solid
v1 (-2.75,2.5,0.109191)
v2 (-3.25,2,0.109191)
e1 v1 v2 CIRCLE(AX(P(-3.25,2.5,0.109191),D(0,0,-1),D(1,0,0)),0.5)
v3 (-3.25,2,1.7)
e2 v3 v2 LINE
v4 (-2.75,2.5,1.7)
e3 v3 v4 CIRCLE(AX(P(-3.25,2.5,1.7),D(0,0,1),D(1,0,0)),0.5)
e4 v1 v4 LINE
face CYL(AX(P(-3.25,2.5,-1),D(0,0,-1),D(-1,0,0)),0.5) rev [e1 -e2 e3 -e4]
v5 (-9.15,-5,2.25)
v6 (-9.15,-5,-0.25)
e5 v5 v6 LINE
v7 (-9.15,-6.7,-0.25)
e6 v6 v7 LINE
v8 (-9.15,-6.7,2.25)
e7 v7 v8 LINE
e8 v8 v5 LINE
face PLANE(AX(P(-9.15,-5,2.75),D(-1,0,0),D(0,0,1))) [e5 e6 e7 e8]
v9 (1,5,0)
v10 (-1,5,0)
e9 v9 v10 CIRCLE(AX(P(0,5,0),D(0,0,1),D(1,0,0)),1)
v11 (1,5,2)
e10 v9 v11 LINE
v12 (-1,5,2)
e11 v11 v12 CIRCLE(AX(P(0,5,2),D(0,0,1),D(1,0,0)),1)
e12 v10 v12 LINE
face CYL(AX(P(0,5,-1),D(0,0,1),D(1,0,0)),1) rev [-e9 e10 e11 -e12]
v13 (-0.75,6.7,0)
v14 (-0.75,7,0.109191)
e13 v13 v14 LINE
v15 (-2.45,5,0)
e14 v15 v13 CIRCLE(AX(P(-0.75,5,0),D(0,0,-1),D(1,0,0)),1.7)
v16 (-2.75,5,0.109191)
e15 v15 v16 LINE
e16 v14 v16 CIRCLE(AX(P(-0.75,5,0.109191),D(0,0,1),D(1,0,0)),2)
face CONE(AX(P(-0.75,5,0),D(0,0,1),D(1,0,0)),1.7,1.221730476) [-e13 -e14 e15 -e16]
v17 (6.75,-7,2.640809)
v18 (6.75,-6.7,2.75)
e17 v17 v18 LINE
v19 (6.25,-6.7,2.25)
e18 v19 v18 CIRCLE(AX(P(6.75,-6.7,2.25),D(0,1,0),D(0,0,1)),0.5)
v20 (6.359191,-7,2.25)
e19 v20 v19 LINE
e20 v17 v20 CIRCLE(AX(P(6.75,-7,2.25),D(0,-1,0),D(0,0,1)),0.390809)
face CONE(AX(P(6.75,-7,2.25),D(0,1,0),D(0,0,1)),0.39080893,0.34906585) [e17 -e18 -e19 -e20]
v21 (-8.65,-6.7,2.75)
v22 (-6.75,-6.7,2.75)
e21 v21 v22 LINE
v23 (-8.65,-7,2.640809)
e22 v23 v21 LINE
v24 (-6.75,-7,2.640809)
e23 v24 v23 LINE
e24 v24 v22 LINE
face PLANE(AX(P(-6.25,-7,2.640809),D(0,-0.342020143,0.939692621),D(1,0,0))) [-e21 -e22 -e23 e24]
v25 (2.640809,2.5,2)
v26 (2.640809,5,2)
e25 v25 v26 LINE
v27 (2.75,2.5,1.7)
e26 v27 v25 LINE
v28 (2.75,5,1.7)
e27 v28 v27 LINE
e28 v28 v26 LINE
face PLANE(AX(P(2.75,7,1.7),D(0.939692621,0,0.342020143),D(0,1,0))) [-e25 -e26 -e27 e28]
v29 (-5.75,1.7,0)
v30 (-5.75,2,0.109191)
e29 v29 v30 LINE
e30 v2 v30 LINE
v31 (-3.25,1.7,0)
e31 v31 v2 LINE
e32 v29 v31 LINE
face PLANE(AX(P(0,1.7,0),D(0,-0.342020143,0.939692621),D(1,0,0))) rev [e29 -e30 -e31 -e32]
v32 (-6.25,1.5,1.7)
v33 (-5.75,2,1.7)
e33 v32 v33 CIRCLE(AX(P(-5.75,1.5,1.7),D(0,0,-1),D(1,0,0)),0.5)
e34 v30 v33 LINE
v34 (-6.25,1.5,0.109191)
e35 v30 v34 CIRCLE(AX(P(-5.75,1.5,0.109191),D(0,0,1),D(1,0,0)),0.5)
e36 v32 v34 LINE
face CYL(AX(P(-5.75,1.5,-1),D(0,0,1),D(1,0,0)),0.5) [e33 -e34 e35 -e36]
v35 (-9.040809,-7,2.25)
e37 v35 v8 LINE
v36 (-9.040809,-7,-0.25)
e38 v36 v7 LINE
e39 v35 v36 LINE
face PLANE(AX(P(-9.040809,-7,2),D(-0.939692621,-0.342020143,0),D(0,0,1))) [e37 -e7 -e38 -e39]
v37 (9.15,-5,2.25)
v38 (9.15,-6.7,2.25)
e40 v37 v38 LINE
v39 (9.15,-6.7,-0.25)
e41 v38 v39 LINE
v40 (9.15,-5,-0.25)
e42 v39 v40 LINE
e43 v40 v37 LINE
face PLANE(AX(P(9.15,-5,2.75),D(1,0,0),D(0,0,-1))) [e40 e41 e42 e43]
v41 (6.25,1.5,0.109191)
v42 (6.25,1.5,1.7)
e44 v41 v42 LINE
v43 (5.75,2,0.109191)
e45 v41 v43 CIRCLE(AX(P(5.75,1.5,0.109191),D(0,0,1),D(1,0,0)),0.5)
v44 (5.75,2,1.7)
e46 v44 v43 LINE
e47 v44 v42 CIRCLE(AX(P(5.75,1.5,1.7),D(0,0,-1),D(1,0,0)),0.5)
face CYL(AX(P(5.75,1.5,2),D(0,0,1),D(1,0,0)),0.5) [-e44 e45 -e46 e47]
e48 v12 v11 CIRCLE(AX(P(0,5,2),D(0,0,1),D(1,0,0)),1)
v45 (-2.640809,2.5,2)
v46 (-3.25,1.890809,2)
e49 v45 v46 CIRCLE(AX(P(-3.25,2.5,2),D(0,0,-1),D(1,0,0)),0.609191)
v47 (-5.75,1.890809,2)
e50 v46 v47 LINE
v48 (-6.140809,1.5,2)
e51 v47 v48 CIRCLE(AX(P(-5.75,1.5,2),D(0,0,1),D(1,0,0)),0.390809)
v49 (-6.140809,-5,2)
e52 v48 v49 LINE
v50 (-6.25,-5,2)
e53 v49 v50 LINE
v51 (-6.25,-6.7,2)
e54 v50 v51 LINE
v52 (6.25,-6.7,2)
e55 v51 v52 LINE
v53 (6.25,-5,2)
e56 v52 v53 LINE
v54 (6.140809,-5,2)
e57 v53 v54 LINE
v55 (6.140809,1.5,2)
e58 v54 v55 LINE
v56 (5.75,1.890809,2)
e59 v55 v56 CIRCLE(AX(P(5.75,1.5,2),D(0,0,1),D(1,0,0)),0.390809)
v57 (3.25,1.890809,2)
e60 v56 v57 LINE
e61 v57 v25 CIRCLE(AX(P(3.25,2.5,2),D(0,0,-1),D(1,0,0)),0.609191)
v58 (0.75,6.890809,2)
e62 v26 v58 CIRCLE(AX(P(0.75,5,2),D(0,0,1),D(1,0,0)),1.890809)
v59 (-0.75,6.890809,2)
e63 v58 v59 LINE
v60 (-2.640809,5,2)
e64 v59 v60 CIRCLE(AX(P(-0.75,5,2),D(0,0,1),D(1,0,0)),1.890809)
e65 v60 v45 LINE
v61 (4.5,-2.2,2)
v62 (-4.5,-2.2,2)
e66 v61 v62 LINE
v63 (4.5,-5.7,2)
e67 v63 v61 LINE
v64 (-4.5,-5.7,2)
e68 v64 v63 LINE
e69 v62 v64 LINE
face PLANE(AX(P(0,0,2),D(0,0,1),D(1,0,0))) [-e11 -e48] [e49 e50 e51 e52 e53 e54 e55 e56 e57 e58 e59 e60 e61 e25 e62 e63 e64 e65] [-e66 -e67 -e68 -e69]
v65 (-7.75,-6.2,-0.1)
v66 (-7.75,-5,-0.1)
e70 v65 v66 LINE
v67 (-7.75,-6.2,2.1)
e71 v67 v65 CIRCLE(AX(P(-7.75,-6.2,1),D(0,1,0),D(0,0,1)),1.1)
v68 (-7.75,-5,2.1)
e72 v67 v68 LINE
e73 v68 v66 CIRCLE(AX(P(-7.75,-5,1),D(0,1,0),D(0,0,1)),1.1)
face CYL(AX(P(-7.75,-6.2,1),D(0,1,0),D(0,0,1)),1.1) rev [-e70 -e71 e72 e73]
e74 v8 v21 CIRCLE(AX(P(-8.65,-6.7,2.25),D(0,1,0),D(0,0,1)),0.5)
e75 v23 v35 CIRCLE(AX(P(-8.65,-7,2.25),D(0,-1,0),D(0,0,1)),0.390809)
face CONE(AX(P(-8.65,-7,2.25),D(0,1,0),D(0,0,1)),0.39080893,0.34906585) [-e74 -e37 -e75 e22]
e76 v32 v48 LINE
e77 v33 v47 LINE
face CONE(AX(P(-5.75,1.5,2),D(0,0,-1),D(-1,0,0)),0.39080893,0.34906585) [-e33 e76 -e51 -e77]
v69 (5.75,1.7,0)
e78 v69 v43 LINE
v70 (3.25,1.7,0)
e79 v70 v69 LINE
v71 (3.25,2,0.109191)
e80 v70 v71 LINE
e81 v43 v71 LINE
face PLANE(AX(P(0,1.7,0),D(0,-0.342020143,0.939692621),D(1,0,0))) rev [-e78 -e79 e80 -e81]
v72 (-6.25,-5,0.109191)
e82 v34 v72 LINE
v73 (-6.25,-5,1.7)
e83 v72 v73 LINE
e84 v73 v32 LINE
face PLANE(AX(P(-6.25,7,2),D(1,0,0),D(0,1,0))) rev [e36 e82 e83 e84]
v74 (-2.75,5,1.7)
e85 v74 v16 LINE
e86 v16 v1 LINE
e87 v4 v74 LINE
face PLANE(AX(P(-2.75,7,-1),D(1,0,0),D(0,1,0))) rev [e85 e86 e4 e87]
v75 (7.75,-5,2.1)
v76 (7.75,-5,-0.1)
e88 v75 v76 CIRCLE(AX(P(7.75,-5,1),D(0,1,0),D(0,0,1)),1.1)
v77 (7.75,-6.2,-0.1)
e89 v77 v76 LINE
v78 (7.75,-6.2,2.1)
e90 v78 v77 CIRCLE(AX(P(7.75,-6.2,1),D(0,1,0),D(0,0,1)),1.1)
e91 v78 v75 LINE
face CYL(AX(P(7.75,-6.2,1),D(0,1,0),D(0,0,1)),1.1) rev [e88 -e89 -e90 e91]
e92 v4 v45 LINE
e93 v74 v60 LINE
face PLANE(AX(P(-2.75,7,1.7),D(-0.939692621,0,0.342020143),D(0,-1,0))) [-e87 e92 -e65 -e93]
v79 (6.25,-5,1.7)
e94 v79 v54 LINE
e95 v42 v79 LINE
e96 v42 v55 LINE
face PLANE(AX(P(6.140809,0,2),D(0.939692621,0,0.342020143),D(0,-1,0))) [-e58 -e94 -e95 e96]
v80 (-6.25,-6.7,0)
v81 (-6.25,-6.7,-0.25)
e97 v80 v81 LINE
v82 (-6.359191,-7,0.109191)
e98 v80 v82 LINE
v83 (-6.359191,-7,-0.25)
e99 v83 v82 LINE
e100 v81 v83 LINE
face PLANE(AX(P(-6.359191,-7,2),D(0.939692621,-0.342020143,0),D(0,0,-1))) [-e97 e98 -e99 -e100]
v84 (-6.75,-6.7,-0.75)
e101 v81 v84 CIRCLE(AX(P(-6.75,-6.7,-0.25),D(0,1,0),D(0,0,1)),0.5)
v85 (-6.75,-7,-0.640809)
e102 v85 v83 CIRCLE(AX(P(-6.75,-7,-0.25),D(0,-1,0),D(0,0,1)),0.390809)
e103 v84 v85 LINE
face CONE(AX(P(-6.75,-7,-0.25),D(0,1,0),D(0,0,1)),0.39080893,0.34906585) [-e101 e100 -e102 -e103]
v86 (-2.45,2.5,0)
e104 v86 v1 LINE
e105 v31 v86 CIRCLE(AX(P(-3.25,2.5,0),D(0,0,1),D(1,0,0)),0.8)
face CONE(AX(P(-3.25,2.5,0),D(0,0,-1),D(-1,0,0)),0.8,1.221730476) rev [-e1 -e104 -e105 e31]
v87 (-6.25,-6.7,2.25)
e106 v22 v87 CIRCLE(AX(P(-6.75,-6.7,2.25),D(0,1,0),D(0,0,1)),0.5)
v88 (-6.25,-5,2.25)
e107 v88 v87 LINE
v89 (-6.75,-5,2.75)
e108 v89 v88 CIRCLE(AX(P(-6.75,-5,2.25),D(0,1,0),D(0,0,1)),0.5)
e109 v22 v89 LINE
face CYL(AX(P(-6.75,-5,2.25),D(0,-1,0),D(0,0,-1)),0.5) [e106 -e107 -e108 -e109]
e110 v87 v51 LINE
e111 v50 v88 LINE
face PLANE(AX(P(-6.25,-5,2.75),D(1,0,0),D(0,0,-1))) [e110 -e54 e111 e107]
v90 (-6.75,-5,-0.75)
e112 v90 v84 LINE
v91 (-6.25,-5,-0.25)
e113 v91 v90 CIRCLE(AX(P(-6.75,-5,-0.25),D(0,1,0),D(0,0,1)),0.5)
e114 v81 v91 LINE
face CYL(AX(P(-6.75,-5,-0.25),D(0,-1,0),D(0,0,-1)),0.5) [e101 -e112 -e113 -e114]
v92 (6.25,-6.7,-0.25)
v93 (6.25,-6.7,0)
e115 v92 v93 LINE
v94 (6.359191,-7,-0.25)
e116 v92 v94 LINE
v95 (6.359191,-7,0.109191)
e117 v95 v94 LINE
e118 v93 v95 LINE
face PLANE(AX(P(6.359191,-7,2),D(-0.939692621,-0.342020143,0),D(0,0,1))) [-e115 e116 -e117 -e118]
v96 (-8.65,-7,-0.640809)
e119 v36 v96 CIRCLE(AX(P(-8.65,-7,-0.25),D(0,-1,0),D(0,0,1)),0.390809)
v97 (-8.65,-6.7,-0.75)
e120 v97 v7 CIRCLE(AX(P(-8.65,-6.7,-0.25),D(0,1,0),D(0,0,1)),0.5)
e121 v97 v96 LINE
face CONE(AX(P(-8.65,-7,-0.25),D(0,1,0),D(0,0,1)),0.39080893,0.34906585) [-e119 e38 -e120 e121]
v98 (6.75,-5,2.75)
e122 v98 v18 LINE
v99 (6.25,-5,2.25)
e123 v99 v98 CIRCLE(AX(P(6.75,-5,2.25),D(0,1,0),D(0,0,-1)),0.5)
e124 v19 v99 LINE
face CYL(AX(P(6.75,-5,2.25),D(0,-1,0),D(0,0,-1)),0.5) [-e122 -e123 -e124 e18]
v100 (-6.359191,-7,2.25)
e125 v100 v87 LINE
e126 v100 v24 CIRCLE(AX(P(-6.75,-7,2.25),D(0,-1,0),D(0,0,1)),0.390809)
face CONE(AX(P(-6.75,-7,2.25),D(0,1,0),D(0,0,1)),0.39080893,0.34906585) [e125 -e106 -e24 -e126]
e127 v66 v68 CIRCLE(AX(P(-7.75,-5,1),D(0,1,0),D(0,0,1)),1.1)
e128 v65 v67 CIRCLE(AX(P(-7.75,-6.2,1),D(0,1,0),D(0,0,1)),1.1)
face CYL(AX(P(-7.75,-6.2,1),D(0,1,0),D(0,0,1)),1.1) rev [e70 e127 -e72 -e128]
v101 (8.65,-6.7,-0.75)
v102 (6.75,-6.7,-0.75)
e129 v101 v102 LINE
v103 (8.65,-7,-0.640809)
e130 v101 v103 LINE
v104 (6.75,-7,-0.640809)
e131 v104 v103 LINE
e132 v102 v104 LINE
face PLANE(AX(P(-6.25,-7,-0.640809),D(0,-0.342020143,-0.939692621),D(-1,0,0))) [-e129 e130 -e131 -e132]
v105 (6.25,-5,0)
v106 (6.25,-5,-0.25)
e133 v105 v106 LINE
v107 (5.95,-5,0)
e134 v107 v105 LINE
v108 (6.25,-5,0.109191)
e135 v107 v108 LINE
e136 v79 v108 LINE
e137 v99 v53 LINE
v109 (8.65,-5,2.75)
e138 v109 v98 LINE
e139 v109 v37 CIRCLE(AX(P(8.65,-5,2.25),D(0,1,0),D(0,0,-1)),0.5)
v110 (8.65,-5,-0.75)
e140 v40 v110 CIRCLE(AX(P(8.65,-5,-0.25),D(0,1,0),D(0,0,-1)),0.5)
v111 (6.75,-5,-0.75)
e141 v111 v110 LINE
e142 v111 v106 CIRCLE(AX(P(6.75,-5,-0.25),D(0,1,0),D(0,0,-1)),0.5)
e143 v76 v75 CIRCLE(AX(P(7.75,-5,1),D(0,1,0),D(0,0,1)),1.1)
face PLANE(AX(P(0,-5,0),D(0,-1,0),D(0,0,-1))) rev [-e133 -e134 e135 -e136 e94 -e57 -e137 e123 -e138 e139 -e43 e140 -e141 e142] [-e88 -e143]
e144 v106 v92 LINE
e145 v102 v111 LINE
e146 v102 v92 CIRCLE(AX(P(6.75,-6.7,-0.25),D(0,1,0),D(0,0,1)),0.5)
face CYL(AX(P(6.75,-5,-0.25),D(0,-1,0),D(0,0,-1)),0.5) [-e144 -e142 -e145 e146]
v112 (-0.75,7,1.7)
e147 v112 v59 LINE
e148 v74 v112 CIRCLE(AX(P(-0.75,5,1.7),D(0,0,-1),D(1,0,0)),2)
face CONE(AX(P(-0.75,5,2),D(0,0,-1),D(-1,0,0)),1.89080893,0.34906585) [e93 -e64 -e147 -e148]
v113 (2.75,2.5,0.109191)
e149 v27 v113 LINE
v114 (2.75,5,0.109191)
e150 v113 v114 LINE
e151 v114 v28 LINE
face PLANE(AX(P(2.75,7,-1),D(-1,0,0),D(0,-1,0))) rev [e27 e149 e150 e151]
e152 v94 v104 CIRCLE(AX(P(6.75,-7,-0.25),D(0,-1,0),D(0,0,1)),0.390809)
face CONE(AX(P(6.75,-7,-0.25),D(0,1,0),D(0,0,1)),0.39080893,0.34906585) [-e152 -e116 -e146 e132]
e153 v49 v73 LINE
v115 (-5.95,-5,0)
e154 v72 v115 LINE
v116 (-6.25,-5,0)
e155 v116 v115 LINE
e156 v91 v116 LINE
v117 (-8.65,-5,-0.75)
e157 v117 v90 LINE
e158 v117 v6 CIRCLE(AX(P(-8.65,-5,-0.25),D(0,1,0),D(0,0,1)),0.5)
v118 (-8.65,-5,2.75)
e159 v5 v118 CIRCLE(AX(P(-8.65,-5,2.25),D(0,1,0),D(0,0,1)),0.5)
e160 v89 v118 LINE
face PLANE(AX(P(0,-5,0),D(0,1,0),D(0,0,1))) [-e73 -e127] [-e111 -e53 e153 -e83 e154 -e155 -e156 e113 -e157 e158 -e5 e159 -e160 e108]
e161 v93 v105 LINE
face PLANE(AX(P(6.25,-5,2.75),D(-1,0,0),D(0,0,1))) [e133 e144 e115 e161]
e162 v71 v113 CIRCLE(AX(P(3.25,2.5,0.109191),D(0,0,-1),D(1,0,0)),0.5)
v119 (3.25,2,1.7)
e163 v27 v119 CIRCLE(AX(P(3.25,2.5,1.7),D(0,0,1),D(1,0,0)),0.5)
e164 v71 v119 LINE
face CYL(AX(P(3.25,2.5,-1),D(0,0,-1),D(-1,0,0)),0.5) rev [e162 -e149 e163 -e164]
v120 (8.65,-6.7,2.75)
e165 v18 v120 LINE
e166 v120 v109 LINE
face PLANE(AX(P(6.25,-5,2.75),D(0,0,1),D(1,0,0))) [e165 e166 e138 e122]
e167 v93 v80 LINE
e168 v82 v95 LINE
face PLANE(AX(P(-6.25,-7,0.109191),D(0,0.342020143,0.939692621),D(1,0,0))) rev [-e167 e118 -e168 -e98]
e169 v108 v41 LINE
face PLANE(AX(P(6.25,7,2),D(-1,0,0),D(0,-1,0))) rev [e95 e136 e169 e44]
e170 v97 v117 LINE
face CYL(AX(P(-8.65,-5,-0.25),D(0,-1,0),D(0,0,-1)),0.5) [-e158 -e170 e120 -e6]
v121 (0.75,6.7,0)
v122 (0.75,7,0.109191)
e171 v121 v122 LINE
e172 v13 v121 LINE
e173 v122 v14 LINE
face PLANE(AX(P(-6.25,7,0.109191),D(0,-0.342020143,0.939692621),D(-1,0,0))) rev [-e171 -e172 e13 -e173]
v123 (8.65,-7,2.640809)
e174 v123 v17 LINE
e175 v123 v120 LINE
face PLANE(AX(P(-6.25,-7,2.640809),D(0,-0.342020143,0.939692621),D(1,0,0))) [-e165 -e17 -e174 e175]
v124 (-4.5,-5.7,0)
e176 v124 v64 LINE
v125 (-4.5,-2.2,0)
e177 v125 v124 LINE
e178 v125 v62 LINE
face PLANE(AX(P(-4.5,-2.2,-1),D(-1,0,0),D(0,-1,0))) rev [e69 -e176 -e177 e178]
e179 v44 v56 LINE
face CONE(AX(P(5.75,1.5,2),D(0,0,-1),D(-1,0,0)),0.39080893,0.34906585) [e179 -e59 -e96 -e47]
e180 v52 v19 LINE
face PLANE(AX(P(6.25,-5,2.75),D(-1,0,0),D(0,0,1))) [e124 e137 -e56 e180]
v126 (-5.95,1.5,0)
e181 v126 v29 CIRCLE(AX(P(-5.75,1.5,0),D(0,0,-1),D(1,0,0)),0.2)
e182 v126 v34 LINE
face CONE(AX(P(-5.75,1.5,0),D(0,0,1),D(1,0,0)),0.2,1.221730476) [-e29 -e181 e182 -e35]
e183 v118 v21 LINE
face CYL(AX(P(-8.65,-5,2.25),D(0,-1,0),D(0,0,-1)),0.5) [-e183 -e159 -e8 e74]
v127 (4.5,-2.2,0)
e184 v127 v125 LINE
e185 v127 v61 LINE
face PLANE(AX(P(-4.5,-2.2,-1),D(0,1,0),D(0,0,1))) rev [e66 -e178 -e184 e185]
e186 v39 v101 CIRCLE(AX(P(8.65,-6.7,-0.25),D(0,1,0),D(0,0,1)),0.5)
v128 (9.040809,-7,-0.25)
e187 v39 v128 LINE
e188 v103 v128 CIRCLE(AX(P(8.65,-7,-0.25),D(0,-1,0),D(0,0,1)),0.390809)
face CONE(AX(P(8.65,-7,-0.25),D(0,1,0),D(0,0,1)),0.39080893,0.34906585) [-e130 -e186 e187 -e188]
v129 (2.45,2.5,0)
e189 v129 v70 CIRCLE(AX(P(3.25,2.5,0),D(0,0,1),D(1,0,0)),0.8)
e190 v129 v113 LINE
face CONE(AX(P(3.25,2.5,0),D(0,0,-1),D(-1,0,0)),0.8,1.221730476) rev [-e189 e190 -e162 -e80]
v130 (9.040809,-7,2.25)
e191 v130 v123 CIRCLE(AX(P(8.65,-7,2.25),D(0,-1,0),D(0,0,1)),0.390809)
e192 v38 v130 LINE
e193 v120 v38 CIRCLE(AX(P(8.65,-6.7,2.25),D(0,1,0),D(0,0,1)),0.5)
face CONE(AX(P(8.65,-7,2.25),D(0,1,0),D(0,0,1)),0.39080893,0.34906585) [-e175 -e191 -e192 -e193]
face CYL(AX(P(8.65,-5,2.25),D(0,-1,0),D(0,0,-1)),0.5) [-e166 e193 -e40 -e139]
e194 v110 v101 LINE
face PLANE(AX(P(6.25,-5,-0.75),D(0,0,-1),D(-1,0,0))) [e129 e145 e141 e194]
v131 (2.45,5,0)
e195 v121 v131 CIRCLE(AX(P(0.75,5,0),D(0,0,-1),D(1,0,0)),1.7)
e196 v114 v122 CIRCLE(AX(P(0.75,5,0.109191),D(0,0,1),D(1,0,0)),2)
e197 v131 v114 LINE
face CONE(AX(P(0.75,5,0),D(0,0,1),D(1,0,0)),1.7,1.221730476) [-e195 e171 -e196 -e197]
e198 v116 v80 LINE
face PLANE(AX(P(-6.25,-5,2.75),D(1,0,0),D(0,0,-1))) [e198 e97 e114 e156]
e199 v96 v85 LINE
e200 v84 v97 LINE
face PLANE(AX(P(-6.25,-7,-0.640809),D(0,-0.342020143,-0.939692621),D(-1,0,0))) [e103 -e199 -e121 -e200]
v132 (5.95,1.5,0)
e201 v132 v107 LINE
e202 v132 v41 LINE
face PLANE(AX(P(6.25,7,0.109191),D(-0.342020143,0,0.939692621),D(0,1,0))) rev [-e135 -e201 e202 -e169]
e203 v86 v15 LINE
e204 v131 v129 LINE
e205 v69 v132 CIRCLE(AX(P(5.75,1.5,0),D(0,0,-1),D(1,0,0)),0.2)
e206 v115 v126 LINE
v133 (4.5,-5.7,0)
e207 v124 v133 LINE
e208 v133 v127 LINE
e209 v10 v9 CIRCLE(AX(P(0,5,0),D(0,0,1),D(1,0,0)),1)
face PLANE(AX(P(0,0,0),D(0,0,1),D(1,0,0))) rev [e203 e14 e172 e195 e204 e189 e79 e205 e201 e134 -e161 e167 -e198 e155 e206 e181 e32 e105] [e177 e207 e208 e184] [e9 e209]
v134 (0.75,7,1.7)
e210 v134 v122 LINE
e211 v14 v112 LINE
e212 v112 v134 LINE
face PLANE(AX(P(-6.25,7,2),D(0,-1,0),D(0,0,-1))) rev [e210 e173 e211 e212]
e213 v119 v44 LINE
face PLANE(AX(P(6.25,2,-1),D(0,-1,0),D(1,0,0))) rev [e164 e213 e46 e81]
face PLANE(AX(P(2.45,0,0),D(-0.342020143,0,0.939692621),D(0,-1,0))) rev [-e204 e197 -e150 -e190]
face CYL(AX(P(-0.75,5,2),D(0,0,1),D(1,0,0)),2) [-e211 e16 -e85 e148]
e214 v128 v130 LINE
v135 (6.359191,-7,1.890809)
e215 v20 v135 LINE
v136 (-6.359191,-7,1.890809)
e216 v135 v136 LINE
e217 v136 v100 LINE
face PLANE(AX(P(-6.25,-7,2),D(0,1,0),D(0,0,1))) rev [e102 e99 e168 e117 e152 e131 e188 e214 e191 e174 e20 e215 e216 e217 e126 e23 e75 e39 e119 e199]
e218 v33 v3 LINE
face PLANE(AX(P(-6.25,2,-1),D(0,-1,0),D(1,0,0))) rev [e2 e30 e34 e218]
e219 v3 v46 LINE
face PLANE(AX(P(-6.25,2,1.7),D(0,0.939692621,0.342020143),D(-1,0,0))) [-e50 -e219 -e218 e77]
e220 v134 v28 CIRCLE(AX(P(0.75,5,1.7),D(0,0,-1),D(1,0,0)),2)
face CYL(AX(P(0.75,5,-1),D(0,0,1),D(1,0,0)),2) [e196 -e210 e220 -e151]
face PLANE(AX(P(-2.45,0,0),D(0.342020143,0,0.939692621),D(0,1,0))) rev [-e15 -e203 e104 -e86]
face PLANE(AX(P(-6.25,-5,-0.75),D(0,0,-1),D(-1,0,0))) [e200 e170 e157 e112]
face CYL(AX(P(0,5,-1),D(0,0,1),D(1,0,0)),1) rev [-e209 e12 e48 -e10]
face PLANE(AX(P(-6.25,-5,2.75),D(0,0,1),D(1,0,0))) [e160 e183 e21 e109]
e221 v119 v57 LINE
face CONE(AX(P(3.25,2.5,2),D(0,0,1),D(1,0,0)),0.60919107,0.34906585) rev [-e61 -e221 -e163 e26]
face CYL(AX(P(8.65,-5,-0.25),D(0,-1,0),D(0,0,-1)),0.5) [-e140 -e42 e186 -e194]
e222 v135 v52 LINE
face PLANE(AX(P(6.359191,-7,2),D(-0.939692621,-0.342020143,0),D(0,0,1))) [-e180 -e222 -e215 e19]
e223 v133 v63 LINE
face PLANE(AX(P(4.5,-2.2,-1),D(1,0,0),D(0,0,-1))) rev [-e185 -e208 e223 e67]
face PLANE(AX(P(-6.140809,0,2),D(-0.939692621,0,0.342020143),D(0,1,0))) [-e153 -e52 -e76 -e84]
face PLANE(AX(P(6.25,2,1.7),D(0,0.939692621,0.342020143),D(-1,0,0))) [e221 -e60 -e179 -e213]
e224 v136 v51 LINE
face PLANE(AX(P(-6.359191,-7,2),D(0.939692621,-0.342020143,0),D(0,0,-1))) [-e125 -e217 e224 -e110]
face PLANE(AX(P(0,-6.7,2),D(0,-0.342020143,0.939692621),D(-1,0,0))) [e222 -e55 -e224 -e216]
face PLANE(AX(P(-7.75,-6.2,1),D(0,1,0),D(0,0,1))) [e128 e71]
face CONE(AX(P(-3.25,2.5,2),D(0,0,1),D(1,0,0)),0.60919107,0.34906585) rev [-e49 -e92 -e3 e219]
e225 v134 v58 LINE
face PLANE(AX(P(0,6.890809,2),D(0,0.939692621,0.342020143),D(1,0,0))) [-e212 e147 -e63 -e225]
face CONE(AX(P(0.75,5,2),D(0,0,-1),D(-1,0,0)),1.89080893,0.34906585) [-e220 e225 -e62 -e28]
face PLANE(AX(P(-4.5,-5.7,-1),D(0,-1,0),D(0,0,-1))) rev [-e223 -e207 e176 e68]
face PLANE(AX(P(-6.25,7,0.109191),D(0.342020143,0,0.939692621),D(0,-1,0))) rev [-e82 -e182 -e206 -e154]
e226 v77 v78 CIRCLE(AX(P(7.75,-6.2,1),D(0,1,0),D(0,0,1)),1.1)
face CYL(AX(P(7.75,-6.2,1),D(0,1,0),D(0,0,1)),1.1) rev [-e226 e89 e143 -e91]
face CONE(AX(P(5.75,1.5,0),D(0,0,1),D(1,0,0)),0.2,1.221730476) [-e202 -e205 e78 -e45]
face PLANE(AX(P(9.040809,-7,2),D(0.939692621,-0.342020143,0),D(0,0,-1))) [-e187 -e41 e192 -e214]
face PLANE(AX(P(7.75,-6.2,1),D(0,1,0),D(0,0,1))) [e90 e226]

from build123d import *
from OCP.BRepFilletAPI import BRepFilletAPI_MakeChamfer

# Parameters (mm, degrees)
SKETCH1_W           = 12.5
SKETCH1_H           = 14
BOSS_EXTRUDE1_DEPTH = 2
SKETCH2_R           = 1
SKETCH2_W           = 9
SKETCH2_H           = 3.5
SKETCH2_W_2         = 3.5
SKETCH2_H_2         = 5
CUT_EXTRUDE1_DEPTH  = 3
FILLET1_R           = 2
SKETCH4_W           = 2.9
SKETCH4_H           = 3.5
BOSS_EXTRUDE2_DEPTH = 2
SKETCH5_R           = 1.1
CUT_EXTRUDE3_DEPTH  = 1.2
FILLET2_R           = 0.5
FILLET3_R           = 0.5
CHAMFER1_SIZE       = 0.3
CHAMFER1_SIZE2      = 0.10919107


with BuildPart() as part:
    # Sketch1 → Boss-Extrude1 (new body)
    with BuildSketch(Plane.XY):
        Rectangle(SKETCH1_W, SKETCH1_H)
    extrude(amount=BOSS_EXTRUDE1_DEPTH)

    # Sketch2 → Cut-Extrude1 (cut)
    with BuildSketch(Plane.XY.offset(2)):
        with Locations((0, 5)):
            Circle(SKETCH2_R)
        with Locations((0, -3.95)):
            Rectangle(SKETCH2_W, SKETCH2_H)
        with Locations((-4.5, 4.5)):
            Rectangle(SKETCH2_W_2, SKETCH2_H_2)
        with Locations((4.5, 4.5)):
            Rectangle(SKETCH2_W_2, SKETCH2_H_2)
    extrude(amount=-CUT_EXTRUDE1_DEPTH, mode=Mode.SUBTRACT)

    # Fillet1
    fillet1_edges = [part.edges().sort_by_distance(p)[0] for p in [
        (-2.75, 7, 1),
        (2.75, 7, 1),
    ]]
    fillet(fillet1_edges, radius=FILLET1_R)

    # Sketch4 → Boss-Extrude2 (add)
    with BuildSketch(Plane.XZ.offset(7)):
        with Locations((-7.7, 1)):
            Rectangle(SKETCH4_W, SKETCH4_H)
        with Locations((7.7, 1)):
            Rectangle(SKETCH4_W, SKETCH4_H)
    extrude(amount=-BOSS_EXTRUDE2_DEPTH)

    # Sketch5 → Cut-Extrude3 (cut)
    with BuildSketch(Plane(origin=(0, -5, 0), x_dir=(1, 0, 0), z_dir=(0, 1, 0))):
        with Locations(Location((-7.75, -1, 0), (0, 0, 270))):
            Circle(SKETCH5_R)
        with Locations(Location((7.75, -1, 0), (0, 0, 270))):
            Circle(SKETCH5_R)
    extrude(amount=-CUT_EXTRUDE3_DEPTH, mode=Mode.SUBTRACT)

    # Fillet2
    fillet2_edges = [part.edges().sort_by_distance(p)[0] for p in [
        (6.25, -6, -0.75),
        (6.25, -6, 2.75),
        (9.15, -6, 2.75),
        (9.15, -6, -0.75),
        (-6.25, 2, 1),
        (6.25, 2, 1),
        (-6.25, -6, 2.75),
        (-6.25, -6, -0.75),
        (-9.15, -6, -0.75),
        (-9.15, -6, 2.75),
    ]]
    fillet(fillet2_edges, radius=FILLET2_R)

    # Fillet3
    fillet3_edges = [part.edges().sort_by_distance(p)[0] for p in [
        (-2.75, 2, 1),
        (2.75, 2, 1),
    ]]
    fillet(fillet3_edges, radius=FILLET3_R)

    # Chamfer1: one chamfer whose edges measure the first distance from different faces: ONE call of the kernel's chamfer builder (chamfer() names one face for all edges)
    chamfer1_edges_1 = [part.edges().sort_by_distance(p)[0] for p in [
        (-9.003553391, -7, -0.603553391),
    ]]
    chamfer1_side_1 = [part.faces().sort_by_distance(p)[0] for p in [
        (-9.003553391, -6, -0.603553391),
    ]]
    chamfer1_edges_2 = [part.edges().sort_by_distance(p)[0] for p in [
        (-9.15, -7, 1),
    ]]
    chamfer1_side_2 = [part.faces().sort_by_distance(p)[0] for p in [
        (-9.15, -6, 1),
    ]]
    chamfer1_edges_3 = [part.edges().sort_by_distance(p)[0] for p in [
        (-9.003553391, -7, 2.603553391),
    ]]
    chamfer1_side_3 = [part.faces().sort_by_distance(p)[0] for p in [
        (-9.003553391, -6, 2.603553391),
    ]]
    chamfer1_edges_4 = [part.edges().sort_by_distance(p)[0] for p in [
        (-7.7, -7, 2.75),
    ]]
    chamfer1_side_4 = [part.faces().sort_by_distance(p)[0] for p in [
        (-7.7, -6, 2.75),
    ]]
    chamfer1_edges_5 = [part.edges().sort_by_distance(p)[0] for p in [
        (-6.396446609, -7, 2.603553391),
    ]]
    chamfer1_side_5 = [part.faces().sort_by_distance(p)[0] for p in [
        (-6.396446609, -6, 2.603553391),
    ]]
    chamfer1_edges_6 = [part.edges().sort_by_distance(p)[0] for p in [
        (-6.25, -7, 2.125),
    ]]
    chamfer1_side_6 = [part.faces().sort_by_distance(p)[0] for p in [
        (-6.25, -6, 2.125),
    ]]
    chamfer1_edges_7 = [part.edges().sort_by_distance(p)[0] for p in [
        (0, -7, 2),
    ]]
    chamfer1_side_7 = [part.faces().sort_by_distance(p)[0] for p in [
        (0, -0.579012096, 2),
    ]]
    chamfer1_edges_8 = [part.edges().sort_by_distance(p)[0] for p in [
        (6.25, -7, 2.125),
    ]]
    chamfer1_side_8 = [part.faces().sort_by_distance(p)[0] for p in [
        (6.25, -6, 2.125),
    ]]
    chamfer1_edges_9 = [part.edges().sort_by_distance(p)[0] for p in [
        (6.396446609, -7, 2.603553391),
    ]]
    chamfer1_side_9 = [part.faces().sort_by_distance(p)[0] for p in [
        (6.396446609, -6, 2.603553391),
    ]]
    chamfer1_edges_10 = [part.edges().sort_by_distance(p)[0] for p in [
        (7.7, -7, 2.75),
    ]]
    chamfer1_side_10 = [part.faces().sort_by_distance(p)[0] for p in [
        (7.7, -6, 2.75),
    ]]
    chamfer1_edges_11 = [part.edges().sort_by_distance(p)[0] for p in [
        (9.003553391, -7, 2.603553391),
    ]]
    chamfer1_side_11 = [part.faces().sort_by_distance(p)[0] for p in [
        (9.003553391, -6, 2.603553391),
    ]]
    chamfer1_edges_12 = [part.edges().sort_by_distance(p)[0] for p in [
        (9.15, -7, 1),
    ]]
    chamfer1_side_12 = [part.faces().sort_by_distance(p)[0] for p in [
        (9.15, -6, 1),
    ]]
    chamfer1_edges_13 = [part.edges().sort_by_distance(p)[0] for p in [
        (9.003553391, -7, -0.603553391),
    ]]
    chamfer1_side_13 = [part.faces().sort_by_distance(p)[0] for p in [
        (9.003553391, -6, -0.603553391),
    ]]
    chamfer1_edges_14 = [part.edges().sort_by_distance(p)[0] for p in [
        (7.7, -7, -0.75),
    ]]
    chamfer1_side_14 = [part.faces().sort_by_distance(p)[0] for p in [
        (7.7, -6, -0.75),
    ]]
    chamfer1_edges_15 = [part.edges().sort_by_distance(p)[0] for p in [
        (6.396446609, -7, -0.603553391),
    ]]
    chamfer1_side_15 = [part.faces().sort_by_distance(p)[0] for p in [
        (6.396446609, -6, -0.603553391),
    ]]
    chamfer1_edges_16 = [part.edges().sort_by_distance(p)[0] for p in [
        (6.25, -7, -0.125),
    ]]
    chamfer1_side_16 = [part.faces().sort_by_distance(p)[0] for p in [
        (6.25, -6, -0.125),
    ]]
    chamfer1_edges_17 = [part.edges().sort_by_distance(p)[0] for p in [
        (0, -7, 0),
        (6.25, -1.75, 0),
        (6.103553391, 1.853553391, 0),
        (2.896446609, 2.146446609, 0),
        (2.75, 3.75, 0),
        (2.164213562, 6.414213562, 0),
        (0, 7, 0),
        (-2.164213562, 6.414213562, 0),
        (-2.75, 3.75, 0),
        (-2.896446609, 2.146446609, 0),
        (-6.103553391, 1.853553391, 0),
        (-6.25, -1.75, 0),
        (4.5, 2, 0),
        (-4.5, 2, 0),
    ]]
    chamfer1_side_17 = [part.faces().sort_by_distance(p)[0] for p in [
        (0, -0.579012096, 0),
    ]]
    chamfer1_edges_18 = [part.edges().sort_by_distance(p)[0] for p in [
        (-6.25, -7, -0.125),
    ]]
    chamfer1_side_18 = [part.faces().sort_by_distance(p)[0] for p in [
        (-6.25, -6, -0.125),
    ]]
    chamfer1_edges_19 = [part.edges().sort_by_distance(p)[0] for p in [
        (-6.396446609, -7, -0.603553391),
    ]]
    chamfer1_side_19 = [part.faces().sort_by_distance(p)[0] for p in [
        (-6.396446609, -6, -0.603553391),
    ]]
    chamfer1_edges_20 = [part.edges().sort_by_distance(p)[0] for p in [
        (-7.7, -7, -0.75),
    ]]
    chamfer1_side_20 = [part.faces().sort_by_distance(p)[0] for p in [
        (-7.7, -6, -0.75),
    ]]
    chamfer1_edges_21 = [part.edges().sort_by_distance(p)[0] for p in [
        (6.25, -1.75, 2),
    ]]
    chamfer1_side_21 = [part.faces().sort_by_distance(p)[0] for p in [
        (6.25, -1.75, 1),
    ]]
    chamfer1_edges_22 = [part.edges().sort_by_distance(p)[0] for p in [
        (6.103553391, 1.853553391, 2),
    ]]
    chamfer1_side_22 = [part.faces().sort_by_distance(p)[0] for p in [
        (6.103553391, 1.853553391, 1),
    ]]
    chamfer1_edges_23 = [part.edges().sort_by_distance(p)[0] for p in [
        (2.896446609, 2.146446609, 2),
    ]]
    chamfer1_side_23 = [part.faces().sort_by_distance(p)[0] for p in [
        (2.896446609, 2.146446609, 1),
    ]]
    chamfer1_edges_24 = [part.edges().sort_by_distance(p)[0] for p in [
        (2.75, 3.75, 2),
    ]]
    chamfer1_side_24 = [part.faces().sort_by_distance(p)[0] for p in [
        (2.75, 3.75, 1),
    ]]
    chamfer1_edges_25 = [part.edges().sort_by_distance(p)[0] for p in [
        (2.164213562, 6.414213562, 2),
    ]]
    chamfer1_side_25 = [part.faces().sort_by_distance(p)[0] for p in [
        (2.164213562, 6.414213562, 1),
    ]]
    chamfer1_edges_26 = [part.edges().sort_by_distance(p)[0] for p in [
        (0, 7, 2),
    ]]
    chamfer1_side_26 = [part.faces().sort_by_distance(p)[0] for p in [
        (0, 7, 1),
    ]]
    chamfer1_edges_27 = [part.edges().sort_by_distance(p)[0] for p in [
        (-2.164213562, 6.414213562, 2),
    ]]
    chamfer1_side_27 = [part.faces().sort_by_distance(p)[0] for p in [
        (-2.164213562, 6.414213562, 1),
    ]]
    chamfer1_edges_28 = [part.edges().sort_by_distance(p)[0] for p in [
        (-2.75, 3.75, 2),
    ]]
    chamfer1_side_28 = [part.faces().sort_by_distance(p)[0] for p in [
        (-2.75, 3.75, 1),
    ]]
    chamfer1_edges_29 = [part.edges().sort_by_distance(p)[0] for p in [
        (-2.896446609, 2.146446609, 2),
    ]]
    chamfer1_side_29 = [part.faces().sort_by_distance(p)[0] for p in [
        (-2.896446609, 2.146446609, 1),
    ]]
    chamfer1_edges_30 = [part.edges().sort_by_distance(p)[0] for p in [
        (-6.103553391, 1.853553391, 2),
    ]]
    chamfer1_side_30 = [part.faces().sort_by_distance(p)[0] for p in [
        (-6.103553391, 1.853553391, 1),
    ]]
    chamfer1_edges_31 = [part.edges().sort_by_distance(p)[0] for p in [
        (-6.25, -1.75, 2),
    ]]
    chamfer1_side_31 = [part.faces().sort_by_distance(p)[0] for p in [
        (-6.25, -1.75, 1),
    ]]
    chamfer1_edges_32 = [part.edges().sort_by_distance(p)[0] for p in [
        (4.5, 2, 2),
    ]]
    chamfer1_side_32 = [part.faces().sort_by_distance(p)[0] for p in [
        (4.5, 2, 1),
    ]]
    chamfer1_edges_33 = [part.edges().sort_by_distance(p)[0] for p in [
        (-4.5, 2, 2),
    ]]
    chamfer1_side_33 = [part.faces().sort_by_distance(p)[0] for p in [
        (-4.5, 2, 1),
    ]]
    chamfer1 = BRepFilletAPI_MakeChamfer(part.part.solid().wrapped)
    for e in chamfer1_edges_1:
        chamfer1.Add(CHAMFER1_SIZE, CHAMFER1_SIZE2, e.wrapped, chamfer1_side_1[0].wrapped)  # the first distance lies on this face
    for e in chamfer1_edges_2:
        chamfer1.Add(CHAMFER1_SIZE, CHAMFER1_SIZE2, e.wrapped, chamfer1_side_2[0].wrapped)  # the first distance lies on this face
    for e in chamfer1_edges_3:
        chamfer1.Add(CHAMFER1_SIZE, CHAMFER1_SIZE2, e.wrapped, chamfer1_side_3[0].wrapped)  # the first distance lies on this face
    for e in chamfer1_edges_4:
        chamfer1.Add(CHAMFER1_SIZE, CHAMFER1_SIZE2, e.wrapped, chamfer1_side_4[0].wrapped)  # the first distance lies on this face
    for e in chamfer1_edges_5:
        chamfer1.Add(CHAMFER1_SIZE, CHAMFER1_SIZE2, e.wrapped, chamfer1_side_5[0].wrapped)  # the first distance lies on this face
    for e in chamfer1_edges_6:
        chamfer1.Add(CHAMFER1_SIZE, CHAMFER1_SIZE2, e.wrapped, chamfer1_side_6[0].wrapped)  # the first distance lies on this face
    for e in chamfer1_edges_7:
        chamfer1.Add(CHAMFER1_SIZE, CHAMFER1_SIZE2, e.wrapped, chamfer1_side_7[0].wrapped)  # the first distance lies on this face
    for e in chamfer1_edges_8:
        chamfer1.Add(CHAMFER1_SIZE, CHAMFER1_SIZE2, e.wrapped, chamfer1_side_8[0].wrapped)  # the first distance lies on this face
    for e in chamfer1_edges_9:
        chamfer1.Add(CHAMFER1_SIZE, CHAMFER1_SIZE2, e.wrapped, chamfer1_side_9[0].wrapped)  # the first distance lies on this face
    for e in chamfer1_edges_10:
        chamfer1.Add(CHAMFER1_SIZE, CHAMFER1_SIZE2, e.wrapped, chamfer1_side_10[0].wrapped)  # the first distance lies on this face
    for e in chamfer1_edges_11:
        chamfer1.Add(CHAMFER1_SIZE, CHAMFER1_SIZE2, e.wrapped, chamfer1_side_11[0].wrapped)  # the first distance lies on this face
    for e in chamfer1_edges_12:
        chamfer1.Add(CHAMFER1_SIZE, CHAMFER1_SIZE2, e.wrapped, chamfer1_side_12[0].wrapped)  # the first distance lies on this face
    for e in chamfer1_edges_13:
        chamfer1.Add(CHAMFER1_SIZE, CHAMFER1_SIZE2, e.wrapped, chamfer1_side_13[0].wrapped)  # the first distance lies on this face
    for e in chamfer1_edges_14:
        chamfer1.Add(CHAMFER1_SIZE, CHAMFER1_SIZE2, e.wrapped, chamfer1_side_14[0].wrapped)  # the first distance lies on this face
    for e in chamfer1_edges_15:
        chamfer1.Add(CHAMFER1_SIZE, CHAMFER1_SIZE2, e.wrapped, chamfer1_side_15[0].wrapped)  # the first distance lies on this face
    for e in chamfer1_edges_16:
        chamfer1.Add(CHAMFER1_SIZE, CHAMFER1_SIZE2, e.wrapped, chamfer1_side_16[0].wrapped)  # the first distance lies on this face
    for e in chamfer1_edges_17:
        chamfer1.Add(CHAMFER1_SIZE, CHAMFER1_SIZE2, e.wrapped, chamfer1_side_17[0].wrapped)  # the first distance lies on this face
    for e in chamfer1_edges_18:
        chamfer1.Add(CHAMFER1_SIZE, CHAMFER1_SIZE2, e.wrapped, chamfer1_side_18[0].wrapped)  # the first distance lies on this face
    for e in chamfer1_edges_19:
        chamfer1.Add(CHAMFER1_SIZE, CHAMFER1_SIZE2, e.wrapped, chamfer1_side_19[0].wrapped)  # the first distance lies on this face
    for e in chamfer1_edges_20:
        chamfer1.Add(CHAMFER1_SIZE, CHAMFER1_SIZE2, e.wrapped, chamfer1_side_20[0].wrapped)  # the first distance lies on this face
    for e in chamfer1_edges_21:
        chamfer1.Add(CHAMFER1_SIZE, CHAMFER1_SIZE2, e.wrapped, chamfer1_side_21[0].wrapped)  # the first distance lies on this face
    for e in chamfer1_edges_22:
        chamfer1.Add(CHAMFER1_SIZE, CHAMFER1_SIZE2, e.wrapped, chamfer1_side_22[0].wrapped)  # the first distance lies on this face
    for e in chamfer1_edges_23:
        chamfer1.Add(CHAMFER1_SIZE, CHAMFER1_SIZE2, e.wrapped, chamfer1_side_23[0].wrapped)  # the first distance lies on this face
    for e in chamfer1_edges_24:
        chamfer1.Add(CHAMFER1_SIZE, CHAMFER1_SIZE2, e.wrapped, chamfer1_side_24[0].wrapped)  # the first distance lies on this face
    for e in chamfer1_edges_25:
        chamfer1.Add(CHAMFER1_SIZE, CHAMFER1_SIZE2, e.wrapped, chamfer1_side_25[0].wrapped)  # the first distance lies on this face
    for e in chamfer1_edges_26:
        chamfer1.Add(CHAMFER1_SIZE, CHAMFER1_SIZE2, e.wrapped, chamfer1_side_26[0].wrapped)  # the first distance lies on this face
    for e in chamfer1_edges_27:
        chamfer1.Add(CHAMFER1_SIZE, CHAMFER1_SIZE2, e.wrapped, chamfer1_side_27[0].wrapped)  # the first distance lies on this face
    for e in chamfer1_edges_28:
        chamfer1.Add(CHAMFER1_SIZE, CHAMFER1_SIZE2, e.wrapped, chamfer1_side_28[0].wrapped)  # the first distance lies on this face
    for e in chamfer1_edges_29:
        chamfer1.Add(CHAMFER1_SIZE, CHAMFER1_SIZE2, e.wrapped, chamfer1_side_29[0].wrapped)  # the first distance lies on this face
    for e in chamfer1_edges_30:
        chamfer1.Add(CHAMFER1_SIZE, CHAMFER1_SIZE2, e.wrapped, chamfer1_side_30[0].wrapped)  # the first distance lies on this face
    for e in chamfer1_edges_31:
        chamfer1.Add(CHAMFER1_SIZE, CHAMFER1_SIZE2, e.wrapped, chamfer1_side_31[0].wrapped)  # the first distance lies on this face
    for e in chamfer1_edges_32:
        chamfer1.Add(CHAMFER1_SIZE, CHAMFER1_SIZE2, e.wrapped, chamfer1_side_32[0].wrapped)  # the first distance lies on this face
    for e in chamfer1_edges_33:
        chamfer1.Add(CHAMFER1_SIZE, CHAMFER1_SIZE2, e.wrapped, chamfer1_side_33[0].wrapped)  # the first distance lies on this face
    add(Compound.cast(chamfer1.Shape()), mode=Mode.REPLACE)


solid = part.part
